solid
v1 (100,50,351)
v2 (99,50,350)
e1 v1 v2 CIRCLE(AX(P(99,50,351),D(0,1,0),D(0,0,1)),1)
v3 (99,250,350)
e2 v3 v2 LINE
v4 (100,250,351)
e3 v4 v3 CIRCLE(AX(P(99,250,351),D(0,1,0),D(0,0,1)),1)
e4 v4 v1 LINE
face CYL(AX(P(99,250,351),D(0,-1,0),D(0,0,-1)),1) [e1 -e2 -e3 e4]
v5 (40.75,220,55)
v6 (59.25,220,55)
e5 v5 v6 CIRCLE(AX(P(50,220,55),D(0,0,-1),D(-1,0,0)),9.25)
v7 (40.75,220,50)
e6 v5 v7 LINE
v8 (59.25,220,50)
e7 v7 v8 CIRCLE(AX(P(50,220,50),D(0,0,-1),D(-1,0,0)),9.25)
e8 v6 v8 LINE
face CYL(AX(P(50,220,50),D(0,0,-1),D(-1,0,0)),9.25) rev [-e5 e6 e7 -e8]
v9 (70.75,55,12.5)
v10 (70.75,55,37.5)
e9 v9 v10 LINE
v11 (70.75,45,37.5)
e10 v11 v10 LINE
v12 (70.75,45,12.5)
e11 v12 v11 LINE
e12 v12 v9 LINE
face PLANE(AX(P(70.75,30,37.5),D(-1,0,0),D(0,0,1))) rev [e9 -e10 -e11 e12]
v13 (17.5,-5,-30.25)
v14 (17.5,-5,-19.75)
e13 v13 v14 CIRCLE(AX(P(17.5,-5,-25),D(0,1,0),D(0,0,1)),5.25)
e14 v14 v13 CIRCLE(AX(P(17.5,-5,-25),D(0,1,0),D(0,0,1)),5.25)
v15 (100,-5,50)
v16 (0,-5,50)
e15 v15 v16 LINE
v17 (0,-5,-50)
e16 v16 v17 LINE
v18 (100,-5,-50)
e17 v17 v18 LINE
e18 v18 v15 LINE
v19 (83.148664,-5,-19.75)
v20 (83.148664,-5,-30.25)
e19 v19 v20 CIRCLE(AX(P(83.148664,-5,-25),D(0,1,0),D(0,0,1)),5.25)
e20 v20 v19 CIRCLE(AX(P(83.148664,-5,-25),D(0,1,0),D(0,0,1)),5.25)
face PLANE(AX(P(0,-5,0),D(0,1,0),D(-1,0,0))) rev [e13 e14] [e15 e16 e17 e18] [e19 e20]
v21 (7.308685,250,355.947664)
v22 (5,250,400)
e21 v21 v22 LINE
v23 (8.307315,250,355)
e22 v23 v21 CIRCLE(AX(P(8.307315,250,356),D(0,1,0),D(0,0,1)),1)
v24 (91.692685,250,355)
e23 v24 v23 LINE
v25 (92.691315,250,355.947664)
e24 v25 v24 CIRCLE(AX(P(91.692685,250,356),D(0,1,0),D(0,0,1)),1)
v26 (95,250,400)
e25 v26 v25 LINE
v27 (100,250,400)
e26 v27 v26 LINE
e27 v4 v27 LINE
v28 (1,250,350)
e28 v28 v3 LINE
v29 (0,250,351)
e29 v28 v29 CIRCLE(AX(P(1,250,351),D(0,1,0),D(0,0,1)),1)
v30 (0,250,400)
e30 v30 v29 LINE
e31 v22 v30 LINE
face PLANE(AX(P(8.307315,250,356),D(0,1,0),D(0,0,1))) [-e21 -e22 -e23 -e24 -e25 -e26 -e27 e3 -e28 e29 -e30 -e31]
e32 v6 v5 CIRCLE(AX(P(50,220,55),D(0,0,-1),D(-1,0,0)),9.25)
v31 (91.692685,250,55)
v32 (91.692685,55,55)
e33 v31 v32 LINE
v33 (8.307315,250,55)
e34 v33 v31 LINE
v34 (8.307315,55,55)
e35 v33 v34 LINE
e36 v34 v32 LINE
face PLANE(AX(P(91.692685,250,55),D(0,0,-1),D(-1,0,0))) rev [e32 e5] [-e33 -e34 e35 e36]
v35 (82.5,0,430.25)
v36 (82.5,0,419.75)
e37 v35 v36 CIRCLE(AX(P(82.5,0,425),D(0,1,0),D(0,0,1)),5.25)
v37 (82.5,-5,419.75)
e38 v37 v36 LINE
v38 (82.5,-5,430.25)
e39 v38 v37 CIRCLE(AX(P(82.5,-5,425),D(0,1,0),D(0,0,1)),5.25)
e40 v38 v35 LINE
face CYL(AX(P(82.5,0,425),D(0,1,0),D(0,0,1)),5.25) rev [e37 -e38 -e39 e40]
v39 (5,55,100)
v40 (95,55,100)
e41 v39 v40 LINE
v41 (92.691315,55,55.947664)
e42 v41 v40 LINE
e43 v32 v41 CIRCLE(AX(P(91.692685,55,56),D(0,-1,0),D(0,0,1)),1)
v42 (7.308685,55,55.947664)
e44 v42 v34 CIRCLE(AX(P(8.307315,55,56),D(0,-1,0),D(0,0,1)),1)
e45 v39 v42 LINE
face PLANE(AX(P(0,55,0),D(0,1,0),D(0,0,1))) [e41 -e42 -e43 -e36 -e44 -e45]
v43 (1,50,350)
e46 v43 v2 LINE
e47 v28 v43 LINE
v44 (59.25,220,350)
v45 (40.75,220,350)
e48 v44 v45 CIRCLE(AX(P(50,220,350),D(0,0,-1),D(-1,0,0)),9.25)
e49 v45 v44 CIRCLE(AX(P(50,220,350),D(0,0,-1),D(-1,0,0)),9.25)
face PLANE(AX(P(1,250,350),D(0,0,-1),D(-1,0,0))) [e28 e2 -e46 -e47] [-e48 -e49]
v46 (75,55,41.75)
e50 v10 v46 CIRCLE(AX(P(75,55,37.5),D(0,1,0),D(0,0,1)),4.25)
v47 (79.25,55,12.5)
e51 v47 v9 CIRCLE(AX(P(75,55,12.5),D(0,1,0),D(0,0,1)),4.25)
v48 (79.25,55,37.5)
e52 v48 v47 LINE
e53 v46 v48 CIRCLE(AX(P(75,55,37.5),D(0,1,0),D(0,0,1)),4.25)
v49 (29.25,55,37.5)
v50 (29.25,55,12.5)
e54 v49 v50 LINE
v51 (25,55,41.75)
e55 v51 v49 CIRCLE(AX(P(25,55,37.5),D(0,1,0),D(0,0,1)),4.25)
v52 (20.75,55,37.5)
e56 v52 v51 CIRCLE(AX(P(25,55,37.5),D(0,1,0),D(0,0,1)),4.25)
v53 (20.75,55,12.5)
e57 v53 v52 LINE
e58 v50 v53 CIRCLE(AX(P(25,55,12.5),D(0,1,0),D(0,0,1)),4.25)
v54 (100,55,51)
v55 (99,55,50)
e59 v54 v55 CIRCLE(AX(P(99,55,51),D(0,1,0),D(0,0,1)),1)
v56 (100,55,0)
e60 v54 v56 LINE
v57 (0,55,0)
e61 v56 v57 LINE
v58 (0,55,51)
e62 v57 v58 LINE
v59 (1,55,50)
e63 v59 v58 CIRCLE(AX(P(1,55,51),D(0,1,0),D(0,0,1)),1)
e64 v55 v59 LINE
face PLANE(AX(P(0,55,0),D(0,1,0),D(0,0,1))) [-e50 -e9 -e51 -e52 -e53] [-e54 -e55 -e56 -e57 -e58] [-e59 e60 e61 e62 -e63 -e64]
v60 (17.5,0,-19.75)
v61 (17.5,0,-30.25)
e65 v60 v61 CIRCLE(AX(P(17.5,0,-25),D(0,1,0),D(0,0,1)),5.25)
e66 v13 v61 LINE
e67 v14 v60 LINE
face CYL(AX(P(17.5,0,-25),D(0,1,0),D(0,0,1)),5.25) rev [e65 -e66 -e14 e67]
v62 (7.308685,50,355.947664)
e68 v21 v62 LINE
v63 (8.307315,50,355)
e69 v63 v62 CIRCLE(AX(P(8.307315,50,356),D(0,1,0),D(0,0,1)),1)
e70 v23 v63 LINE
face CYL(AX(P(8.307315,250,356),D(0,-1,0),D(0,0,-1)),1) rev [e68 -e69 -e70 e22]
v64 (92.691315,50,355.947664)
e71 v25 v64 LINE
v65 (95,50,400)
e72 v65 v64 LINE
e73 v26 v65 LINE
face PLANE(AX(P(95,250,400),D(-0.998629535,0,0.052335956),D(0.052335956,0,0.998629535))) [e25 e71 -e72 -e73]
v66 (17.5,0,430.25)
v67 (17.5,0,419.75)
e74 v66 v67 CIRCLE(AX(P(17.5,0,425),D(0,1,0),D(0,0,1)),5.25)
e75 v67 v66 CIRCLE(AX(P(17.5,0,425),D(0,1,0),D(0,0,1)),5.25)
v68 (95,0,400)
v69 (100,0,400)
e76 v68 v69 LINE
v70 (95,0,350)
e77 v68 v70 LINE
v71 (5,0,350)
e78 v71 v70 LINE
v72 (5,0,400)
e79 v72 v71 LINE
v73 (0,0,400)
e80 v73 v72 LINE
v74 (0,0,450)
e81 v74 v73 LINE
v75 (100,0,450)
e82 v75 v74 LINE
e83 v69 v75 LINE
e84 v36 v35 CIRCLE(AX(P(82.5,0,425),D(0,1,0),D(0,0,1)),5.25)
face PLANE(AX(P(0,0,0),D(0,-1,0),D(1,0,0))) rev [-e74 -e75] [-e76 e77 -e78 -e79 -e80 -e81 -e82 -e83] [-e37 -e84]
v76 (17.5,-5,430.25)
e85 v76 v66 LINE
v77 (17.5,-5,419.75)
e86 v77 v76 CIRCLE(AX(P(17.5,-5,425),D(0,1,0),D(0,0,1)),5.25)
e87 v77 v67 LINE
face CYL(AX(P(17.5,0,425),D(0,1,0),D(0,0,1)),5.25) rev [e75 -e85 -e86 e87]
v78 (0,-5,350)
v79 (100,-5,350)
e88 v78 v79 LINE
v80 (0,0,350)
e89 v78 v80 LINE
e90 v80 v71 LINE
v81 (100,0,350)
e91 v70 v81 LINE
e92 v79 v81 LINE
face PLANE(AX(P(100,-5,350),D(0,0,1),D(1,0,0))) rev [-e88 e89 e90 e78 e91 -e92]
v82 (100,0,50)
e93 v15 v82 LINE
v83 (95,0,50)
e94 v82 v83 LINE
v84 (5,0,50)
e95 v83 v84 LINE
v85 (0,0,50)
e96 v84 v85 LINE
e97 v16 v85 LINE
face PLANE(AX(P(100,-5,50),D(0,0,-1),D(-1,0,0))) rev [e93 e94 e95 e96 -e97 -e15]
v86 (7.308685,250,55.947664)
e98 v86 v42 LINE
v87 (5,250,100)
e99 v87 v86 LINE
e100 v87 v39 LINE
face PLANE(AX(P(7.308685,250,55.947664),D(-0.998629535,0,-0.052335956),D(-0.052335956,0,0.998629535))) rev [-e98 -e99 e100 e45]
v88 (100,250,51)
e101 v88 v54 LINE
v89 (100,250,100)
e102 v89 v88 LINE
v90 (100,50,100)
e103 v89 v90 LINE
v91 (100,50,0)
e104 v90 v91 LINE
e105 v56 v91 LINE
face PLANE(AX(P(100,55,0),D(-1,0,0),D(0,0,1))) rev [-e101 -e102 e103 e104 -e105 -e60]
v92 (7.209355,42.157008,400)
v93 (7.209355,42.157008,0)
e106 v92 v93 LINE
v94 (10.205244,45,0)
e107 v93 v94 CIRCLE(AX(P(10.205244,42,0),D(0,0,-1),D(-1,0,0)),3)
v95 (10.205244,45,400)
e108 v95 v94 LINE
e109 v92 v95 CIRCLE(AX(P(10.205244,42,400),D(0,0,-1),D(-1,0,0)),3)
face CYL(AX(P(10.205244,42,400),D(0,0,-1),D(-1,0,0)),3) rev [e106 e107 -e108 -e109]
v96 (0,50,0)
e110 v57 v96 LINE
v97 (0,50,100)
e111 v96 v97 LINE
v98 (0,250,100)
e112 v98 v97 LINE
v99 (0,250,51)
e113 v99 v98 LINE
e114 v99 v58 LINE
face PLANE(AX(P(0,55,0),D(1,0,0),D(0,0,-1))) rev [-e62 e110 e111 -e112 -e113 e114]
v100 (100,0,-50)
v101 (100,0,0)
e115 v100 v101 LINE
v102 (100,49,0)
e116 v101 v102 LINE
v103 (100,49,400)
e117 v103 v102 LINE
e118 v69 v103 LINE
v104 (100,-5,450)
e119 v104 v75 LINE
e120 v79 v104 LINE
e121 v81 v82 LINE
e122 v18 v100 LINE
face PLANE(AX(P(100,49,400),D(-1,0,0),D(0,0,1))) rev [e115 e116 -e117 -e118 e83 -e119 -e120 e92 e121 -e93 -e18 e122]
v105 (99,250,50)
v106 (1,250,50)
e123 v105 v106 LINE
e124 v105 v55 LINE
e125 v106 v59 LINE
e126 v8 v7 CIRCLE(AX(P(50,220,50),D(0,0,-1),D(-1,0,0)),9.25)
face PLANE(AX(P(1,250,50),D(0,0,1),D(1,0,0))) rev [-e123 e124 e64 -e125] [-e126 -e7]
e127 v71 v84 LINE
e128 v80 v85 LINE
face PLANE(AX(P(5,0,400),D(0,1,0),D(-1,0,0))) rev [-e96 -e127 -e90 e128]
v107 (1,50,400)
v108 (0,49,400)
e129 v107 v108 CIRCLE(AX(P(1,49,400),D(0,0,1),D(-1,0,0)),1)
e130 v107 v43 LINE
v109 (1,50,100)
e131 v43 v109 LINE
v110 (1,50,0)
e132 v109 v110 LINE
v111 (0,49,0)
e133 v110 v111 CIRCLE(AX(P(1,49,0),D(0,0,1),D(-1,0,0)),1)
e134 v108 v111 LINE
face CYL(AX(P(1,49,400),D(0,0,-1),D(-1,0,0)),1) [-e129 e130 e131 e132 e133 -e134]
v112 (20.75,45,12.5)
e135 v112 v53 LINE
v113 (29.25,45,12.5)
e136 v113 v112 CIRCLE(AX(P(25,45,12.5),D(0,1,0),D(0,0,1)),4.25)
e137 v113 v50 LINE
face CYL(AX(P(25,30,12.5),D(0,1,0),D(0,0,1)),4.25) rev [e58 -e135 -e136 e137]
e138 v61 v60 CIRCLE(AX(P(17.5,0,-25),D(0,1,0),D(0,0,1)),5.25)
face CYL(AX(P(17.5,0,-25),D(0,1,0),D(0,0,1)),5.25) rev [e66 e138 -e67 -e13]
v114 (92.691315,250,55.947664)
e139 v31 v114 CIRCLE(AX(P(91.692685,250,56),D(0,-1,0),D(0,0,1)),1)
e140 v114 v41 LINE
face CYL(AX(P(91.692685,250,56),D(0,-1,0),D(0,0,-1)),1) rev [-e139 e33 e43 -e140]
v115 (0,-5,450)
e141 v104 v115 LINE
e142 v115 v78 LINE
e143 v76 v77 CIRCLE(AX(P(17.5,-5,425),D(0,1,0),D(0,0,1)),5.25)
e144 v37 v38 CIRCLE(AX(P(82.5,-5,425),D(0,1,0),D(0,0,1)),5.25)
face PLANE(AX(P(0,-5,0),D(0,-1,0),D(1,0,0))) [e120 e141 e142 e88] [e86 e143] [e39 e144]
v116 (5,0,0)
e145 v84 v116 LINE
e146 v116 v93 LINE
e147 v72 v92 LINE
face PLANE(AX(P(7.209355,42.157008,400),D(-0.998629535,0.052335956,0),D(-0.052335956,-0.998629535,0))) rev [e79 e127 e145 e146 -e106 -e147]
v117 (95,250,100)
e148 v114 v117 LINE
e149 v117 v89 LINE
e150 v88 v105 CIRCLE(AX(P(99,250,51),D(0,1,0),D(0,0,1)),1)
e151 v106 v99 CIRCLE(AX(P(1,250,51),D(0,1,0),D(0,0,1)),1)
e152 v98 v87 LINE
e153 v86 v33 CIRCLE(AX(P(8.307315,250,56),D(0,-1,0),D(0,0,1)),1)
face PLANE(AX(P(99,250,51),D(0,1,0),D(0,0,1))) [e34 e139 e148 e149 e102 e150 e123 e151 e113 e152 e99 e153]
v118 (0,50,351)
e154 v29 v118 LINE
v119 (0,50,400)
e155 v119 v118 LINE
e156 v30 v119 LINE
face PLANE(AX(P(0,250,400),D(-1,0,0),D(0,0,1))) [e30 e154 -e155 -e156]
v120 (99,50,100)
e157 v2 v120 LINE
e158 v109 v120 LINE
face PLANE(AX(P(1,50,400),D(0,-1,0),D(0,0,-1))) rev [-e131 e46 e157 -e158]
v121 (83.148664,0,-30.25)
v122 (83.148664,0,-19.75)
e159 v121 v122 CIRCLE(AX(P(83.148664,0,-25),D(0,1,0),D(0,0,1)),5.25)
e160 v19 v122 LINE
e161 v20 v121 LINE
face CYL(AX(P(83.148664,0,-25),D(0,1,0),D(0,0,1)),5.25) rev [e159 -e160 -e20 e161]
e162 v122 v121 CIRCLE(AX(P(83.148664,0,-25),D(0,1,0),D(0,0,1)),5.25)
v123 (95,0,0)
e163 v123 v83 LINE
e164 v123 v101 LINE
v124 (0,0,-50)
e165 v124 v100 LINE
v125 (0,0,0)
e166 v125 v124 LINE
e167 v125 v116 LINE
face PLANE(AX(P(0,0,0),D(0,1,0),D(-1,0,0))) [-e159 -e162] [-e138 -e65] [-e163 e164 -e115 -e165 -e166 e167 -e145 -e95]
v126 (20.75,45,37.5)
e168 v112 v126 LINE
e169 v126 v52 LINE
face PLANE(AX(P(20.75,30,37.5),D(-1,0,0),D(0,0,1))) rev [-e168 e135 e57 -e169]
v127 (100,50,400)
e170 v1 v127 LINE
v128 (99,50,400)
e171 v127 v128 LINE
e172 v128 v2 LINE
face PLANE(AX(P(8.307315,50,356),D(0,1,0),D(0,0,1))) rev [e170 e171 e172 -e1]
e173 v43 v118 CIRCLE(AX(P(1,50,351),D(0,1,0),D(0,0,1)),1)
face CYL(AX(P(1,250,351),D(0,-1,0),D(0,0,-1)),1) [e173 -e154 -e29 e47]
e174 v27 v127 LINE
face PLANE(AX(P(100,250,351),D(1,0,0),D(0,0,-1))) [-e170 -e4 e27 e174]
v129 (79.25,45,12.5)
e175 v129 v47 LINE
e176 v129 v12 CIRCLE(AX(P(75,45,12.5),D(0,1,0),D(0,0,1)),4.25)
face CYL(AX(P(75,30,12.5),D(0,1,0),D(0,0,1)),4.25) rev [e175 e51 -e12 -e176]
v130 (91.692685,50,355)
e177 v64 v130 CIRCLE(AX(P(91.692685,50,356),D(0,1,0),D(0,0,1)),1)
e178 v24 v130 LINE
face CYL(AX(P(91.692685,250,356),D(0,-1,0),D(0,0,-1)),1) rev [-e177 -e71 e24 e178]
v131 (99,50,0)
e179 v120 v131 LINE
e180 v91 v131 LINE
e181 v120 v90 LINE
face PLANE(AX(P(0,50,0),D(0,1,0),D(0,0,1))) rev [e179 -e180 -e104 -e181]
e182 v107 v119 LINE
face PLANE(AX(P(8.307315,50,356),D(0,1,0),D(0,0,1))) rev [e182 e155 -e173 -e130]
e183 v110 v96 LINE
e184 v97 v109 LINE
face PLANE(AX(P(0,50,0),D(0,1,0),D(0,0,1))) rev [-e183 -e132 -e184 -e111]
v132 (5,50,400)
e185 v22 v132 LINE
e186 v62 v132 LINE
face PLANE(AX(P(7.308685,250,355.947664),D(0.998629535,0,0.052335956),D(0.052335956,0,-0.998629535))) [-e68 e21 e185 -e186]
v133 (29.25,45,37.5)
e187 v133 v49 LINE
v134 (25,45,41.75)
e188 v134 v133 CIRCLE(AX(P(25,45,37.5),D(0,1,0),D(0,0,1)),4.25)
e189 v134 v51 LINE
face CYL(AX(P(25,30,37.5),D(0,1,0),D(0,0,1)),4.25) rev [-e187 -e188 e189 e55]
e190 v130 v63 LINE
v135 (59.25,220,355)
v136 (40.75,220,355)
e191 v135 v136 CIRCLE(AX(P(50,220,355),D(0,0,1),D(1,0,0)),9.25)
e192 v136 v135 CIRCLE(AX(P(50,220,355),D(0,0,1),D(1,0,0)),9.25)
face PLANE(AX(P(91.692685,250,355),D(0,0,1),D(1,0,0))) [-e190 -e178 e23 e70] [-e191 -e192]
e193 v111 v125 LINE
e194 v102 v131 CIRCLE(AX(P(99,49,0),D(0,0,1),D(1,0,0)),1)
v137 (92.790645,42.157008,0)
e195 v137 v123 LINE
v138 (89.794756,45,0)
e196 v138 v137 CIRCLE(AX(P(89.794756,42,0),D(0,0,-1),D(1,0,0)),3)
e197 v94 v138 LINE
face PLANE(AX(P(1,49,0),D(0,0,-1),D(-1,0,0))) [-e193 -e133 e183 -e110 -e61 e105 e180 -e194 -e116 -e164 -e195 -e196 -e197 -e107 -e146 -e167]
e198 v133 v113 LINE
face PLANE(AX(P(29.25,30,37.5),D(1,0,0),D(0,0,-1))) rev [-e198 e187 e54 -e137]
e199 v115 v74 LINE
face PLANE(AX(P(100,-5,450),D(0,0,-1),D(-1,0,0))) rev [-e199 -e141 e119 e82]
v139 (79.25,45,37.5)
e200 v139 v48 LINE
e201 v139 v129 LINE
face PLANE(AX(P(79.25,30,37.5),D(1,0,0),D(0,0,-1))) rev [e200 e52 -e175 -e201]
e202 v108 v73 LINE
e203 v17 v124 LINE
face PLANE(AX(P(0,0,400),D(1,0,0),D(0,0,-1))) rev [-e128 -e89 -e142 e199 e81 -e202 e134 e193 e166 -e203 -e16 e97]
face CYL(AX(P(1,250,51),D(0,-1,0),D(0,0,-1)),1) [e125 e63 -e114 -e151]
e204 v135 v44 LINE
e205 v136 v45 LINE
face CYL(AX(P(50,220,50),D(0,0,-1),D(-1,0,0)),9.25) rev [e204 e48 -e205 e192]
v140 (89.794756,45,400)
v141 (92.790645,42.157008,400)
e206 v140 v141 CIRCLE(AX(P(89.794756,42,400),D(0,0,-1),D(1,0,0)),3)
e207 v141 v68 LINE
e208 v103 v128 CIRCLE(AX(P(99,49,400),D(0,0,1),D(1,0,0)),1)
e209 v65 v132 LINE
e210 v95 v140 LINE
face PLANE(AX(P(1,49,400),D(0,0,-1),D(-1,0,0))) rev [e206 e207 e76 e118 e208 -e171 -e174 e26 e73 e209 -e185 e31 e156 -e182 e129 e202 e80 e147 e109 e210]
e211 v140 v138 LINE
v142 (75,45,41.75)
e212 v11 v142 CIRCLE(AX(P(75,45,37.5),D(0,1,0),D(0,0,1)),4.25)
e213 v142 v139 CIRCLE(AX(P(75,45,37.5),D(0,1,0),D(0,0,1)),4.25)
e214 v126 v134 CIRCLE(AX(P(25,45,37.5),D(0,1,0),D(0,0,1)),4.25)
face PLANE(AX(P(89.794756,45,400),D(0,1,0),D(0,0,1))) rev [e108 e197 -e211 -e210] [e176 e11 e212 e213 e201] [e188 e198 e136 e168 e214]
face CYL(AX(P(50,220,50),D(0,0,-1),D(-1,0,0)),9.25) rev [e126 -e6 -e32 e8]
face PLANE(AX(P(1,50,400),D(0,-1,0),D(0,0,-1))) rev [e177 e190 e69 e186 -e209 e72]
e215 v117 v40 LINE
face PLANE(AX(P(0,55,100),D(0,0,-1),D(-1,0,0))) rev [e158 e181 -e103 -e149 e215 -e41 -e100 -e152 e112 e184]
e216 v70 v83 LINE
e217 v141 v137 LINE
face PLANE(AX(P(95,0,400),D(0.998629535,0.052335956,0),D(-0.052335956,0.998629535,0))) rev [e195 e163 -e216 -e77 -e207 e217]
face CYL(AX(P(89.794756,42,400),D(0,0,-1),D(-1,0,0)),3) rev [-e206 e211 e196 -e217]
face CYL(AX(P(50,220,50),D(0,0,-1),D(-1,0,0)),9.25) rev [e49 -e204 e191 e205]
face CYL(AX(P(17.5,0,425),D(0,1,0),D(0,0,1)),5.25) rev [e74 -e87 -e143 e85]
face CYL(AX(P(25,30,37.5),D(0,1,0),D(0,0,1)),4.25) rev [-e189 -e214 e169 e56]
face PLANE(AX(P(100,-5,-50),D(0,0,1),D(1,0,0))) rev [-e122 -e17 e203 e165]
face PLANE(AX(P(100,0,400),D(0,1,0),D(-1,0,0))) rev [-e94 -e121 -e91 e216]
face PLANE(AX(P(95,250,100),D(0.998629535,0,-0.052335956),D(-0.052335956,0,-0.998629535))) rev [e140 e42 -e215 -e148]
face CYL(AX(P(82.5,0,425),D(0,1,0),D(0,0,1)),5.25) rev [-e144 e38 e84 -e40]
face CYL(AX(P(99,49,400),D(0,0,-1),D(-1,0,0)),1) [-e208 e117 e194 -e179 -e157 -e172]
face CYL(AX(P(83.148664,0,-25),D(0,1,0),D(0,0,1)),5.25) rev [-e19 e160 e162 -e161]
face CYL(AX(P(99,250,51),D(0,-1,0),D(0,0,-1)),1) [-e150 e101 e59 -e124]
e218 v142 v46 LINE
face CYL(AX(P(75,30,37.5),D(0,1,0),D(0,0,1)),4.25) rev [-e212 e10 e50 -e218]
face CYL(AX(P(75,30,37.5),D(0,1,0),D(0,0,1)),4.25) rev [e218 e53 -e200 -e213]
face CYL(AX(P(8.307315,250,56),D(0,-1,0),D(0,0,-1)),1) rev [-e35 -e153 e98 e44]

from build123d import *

# Parameters (mm, degrees)
BOSS_EXTRUDE1_DEPTH          = 400
SKETCH2_W                    = 100
SKETCH2_H                    = 100
BOSS_EXTRUDE2_DEPTH          = 5
F_10_5_10_5_DIAMETER_HOLE1_D = 10.5
BOSS_EXTRUDE3_DEPTH          = 200
SKETCH6_W                    = 100
SKETCH6_H                    = 100
BOSS_EXTRUDE4_DEPTH          = 5
BOSS_EXTRUDE5_DEPTH          = 195
CUT_EXTRUDE1_DEPTH           = 20
CUT_EXTRUDE1_DEPTH_BACK      = 20
F_18_5_18_5_DIAMETER_HOLE1_D = 18.5


with BuildPart() as part:
    # Sketch1 → Boss-Extrude1 (new body)
    with BuildSketch(Plane.XY):
        with BuildLine():
            Line((0, 0), (0, 49))
            ThreePointArc((0, 49), (0.292893219, 49.707106781), (1, 50))
            Line((1, 50), (99, 50))
            ThreePointArc((99, 50), (99.707106781, 49.707106781), (100, 49))
            Line((100, 49), (100, 0))
            Line((100, 0), (95, 0))
            Line((95, 0), (92.790644836, 42.157007869))
            ThreePointArc((92.790644836, 42.157007869), (91.859819959, 44.176123113), (89.794756232, 45))
            Line((89.794756232, 45), (10.205243768, 45))
            ThreePointArc((10.205243768, 45), (8.140180041, 44.176123113), (7.209355164, 42.157007869))
            Line((7.209355164, 42.157007869), (5, 0))
            Line((5, 0), (0, 0))
        make_face()
    extrude(amount=BOSS_EXTRUDE1_DEPTH)

    # Sketch2 → Boss-Extrude2 (add)
    with BuildSketch(Plane.XZ):
        with Locations((50, 400)):
            Rectangle(SKETCH2_W, SKETCH2_H)
        with Locations((50, 0)):
            Rectangle(SKETCH2_W, SKETCH2_H)
    extrude(amount=BOSS_EXTRUDE2_DEPTH)

    # Ø10.5 (10.5) Diameter Hole1 (through all)
    with Locations(Plane(origin=(0, 0, 0), x_dir=(1, 0, 0), z_dir=(0, 1, 0))):
        with Locations((17.5, -425), (82.5, -425), (83.148664141, 25), (17.5, 25)):
            Hole(F_10_5_10_5_DIAMETER_HOLE1_D / 2)

    # Sketch5 → Boss-Extrude3 (add)
    with BuildSketch(Plane(origin=(0, 50, 0), x_dir=(1, 0, 0), z_dir=(0, 1, 0))):
        with BuildLine():
            Line((1, -350), (99, -350))
            ThreePointArc((99, -350), (99.707106781, -350.292893219), (100, -351))
            Line((100, -351), (100, -400))
            Line((100, -400), (95, -400))
            Line((95, -400), (92.6913149, -355.947664044))
            ThreePointArc((92.6913149, -355.947664044), (92.381039941, -355.274625629), (91.692685366, -355))
            Line((91.692685366, -355), (8.307314634, -355))
            ThreePointArc((8.307314634, -355), (7.618960059, -355.274625629), (7.3086851, -355.947664044))
            Line((7.3086851, -355.947664044), (5, -400))
            Line((5, -400), (0, -400))
            Line((0, -400), (0, -351))
            ThreePointArc((0, -351), (0.292893219, -350.292893219), (1, -350))
        make_face()
    extrude(amount=BOSS_EXTRUDE3_DEPTH)

    # Sketch6 → Boss-Extrude4 (add)
    with BuildSketch(Plane(origin=(0, 50, 0), x_dir=(1, 0, 0), z_dir=(0, 1, 0))):
        with Locations((50, -50)):
            Rectangle(SKETCH6_W, SKETCH6_H)
    extrude(amount=BOSS_EXTRUDE4_DEPTH)

    # Sketch7 → Boss-Extrude5 (add)
    with BuildSketch(Plane(origin=(0, 55, 0), x_dir=(1, 0, 0), z_dir=(0, 1, 0))):
        with BuildLine():
            Line((1, -50), (99, -50))
            ThreePointArc((99, -50), (99.707106781, -50.292893219), (100, -51))
            Line((100, -51), (100, -100))
            Line((100, -100), (95, -100))
            Line((95, -100), (92.6913149, -55.947664044))
            ThreePointArc((92.6913149, -55.947664044), (92.381039941, -55.274625629), (91.692685366, -55))
            Line((91.692685366, -55), (8.307314634, -55))
            ThreePointArc((8.307314634, -55), (7.618960059, -55.274625629), (7.3086851, -55.947664044))
            Line((7.3086851, -55.947664044), (5, -100))
            Line((5, -100), (0, -100))
            Line((0, -100), (0, -51))
            ThreePointArc((0, -51), (0.292893219, -50.292893219), (1, -50))
        make_face()
    extrude(amount=BOSS_EXTRUDE5_DEPTH)

    # Sketch8 → Cut-Extrude1 (cut, two sides: drawn at the far end of the back side and taken through both)
    with BuildSketch(Plane(origin=(0, 50, 0), x_dir=(1, 0, 0), z_dir=(0, 1, 0)).offset(-CUT_EXTRUDE1_DEPTH_BACK)):
        with BuildLine():
            Line((20.75, -37.5), (20.75, -12.5))
            ThreePointArc((20.75, -12.5), (25, -8.25), (29.25, -12.5))
            Line((29.25, -12.5), (29.25, -37.5))
            ThreePointArc((29.25, -37.5), (25, -41.75), (20.75, -37.5))
        make_face()
        with BuildLine():
            Line((70.75, -37.5), (70.75, -12.5))
            ThreePointArc((70.75, -12.5), (75, -8.25), (79.25, -12.5))
            Line((79.25, -12.5), (79.25, -37.5))
            ThreePointArc((79.25, -37.5), (75, -41.75), (70.75, -37.5))
        make_face()
    extrude(amount=CUT_EXTRUDE1_DEPTH + CUT_EXTRUDE1_DEPTH_BACK, mode=Mode.SUBTRACT)

    # Ø18.5 (18.5) Diameter Hole1 (through all)
    with Locations(Plane(origin=(0, 0, 50), x_dir=(-1, 0, 0), z_dir=(0, 0, -1))):
        with Locations((-50, 220)):
            Hole(F_18_5_18_5_DIAMETER_HOLE1_D / 2)


solid = part.part
